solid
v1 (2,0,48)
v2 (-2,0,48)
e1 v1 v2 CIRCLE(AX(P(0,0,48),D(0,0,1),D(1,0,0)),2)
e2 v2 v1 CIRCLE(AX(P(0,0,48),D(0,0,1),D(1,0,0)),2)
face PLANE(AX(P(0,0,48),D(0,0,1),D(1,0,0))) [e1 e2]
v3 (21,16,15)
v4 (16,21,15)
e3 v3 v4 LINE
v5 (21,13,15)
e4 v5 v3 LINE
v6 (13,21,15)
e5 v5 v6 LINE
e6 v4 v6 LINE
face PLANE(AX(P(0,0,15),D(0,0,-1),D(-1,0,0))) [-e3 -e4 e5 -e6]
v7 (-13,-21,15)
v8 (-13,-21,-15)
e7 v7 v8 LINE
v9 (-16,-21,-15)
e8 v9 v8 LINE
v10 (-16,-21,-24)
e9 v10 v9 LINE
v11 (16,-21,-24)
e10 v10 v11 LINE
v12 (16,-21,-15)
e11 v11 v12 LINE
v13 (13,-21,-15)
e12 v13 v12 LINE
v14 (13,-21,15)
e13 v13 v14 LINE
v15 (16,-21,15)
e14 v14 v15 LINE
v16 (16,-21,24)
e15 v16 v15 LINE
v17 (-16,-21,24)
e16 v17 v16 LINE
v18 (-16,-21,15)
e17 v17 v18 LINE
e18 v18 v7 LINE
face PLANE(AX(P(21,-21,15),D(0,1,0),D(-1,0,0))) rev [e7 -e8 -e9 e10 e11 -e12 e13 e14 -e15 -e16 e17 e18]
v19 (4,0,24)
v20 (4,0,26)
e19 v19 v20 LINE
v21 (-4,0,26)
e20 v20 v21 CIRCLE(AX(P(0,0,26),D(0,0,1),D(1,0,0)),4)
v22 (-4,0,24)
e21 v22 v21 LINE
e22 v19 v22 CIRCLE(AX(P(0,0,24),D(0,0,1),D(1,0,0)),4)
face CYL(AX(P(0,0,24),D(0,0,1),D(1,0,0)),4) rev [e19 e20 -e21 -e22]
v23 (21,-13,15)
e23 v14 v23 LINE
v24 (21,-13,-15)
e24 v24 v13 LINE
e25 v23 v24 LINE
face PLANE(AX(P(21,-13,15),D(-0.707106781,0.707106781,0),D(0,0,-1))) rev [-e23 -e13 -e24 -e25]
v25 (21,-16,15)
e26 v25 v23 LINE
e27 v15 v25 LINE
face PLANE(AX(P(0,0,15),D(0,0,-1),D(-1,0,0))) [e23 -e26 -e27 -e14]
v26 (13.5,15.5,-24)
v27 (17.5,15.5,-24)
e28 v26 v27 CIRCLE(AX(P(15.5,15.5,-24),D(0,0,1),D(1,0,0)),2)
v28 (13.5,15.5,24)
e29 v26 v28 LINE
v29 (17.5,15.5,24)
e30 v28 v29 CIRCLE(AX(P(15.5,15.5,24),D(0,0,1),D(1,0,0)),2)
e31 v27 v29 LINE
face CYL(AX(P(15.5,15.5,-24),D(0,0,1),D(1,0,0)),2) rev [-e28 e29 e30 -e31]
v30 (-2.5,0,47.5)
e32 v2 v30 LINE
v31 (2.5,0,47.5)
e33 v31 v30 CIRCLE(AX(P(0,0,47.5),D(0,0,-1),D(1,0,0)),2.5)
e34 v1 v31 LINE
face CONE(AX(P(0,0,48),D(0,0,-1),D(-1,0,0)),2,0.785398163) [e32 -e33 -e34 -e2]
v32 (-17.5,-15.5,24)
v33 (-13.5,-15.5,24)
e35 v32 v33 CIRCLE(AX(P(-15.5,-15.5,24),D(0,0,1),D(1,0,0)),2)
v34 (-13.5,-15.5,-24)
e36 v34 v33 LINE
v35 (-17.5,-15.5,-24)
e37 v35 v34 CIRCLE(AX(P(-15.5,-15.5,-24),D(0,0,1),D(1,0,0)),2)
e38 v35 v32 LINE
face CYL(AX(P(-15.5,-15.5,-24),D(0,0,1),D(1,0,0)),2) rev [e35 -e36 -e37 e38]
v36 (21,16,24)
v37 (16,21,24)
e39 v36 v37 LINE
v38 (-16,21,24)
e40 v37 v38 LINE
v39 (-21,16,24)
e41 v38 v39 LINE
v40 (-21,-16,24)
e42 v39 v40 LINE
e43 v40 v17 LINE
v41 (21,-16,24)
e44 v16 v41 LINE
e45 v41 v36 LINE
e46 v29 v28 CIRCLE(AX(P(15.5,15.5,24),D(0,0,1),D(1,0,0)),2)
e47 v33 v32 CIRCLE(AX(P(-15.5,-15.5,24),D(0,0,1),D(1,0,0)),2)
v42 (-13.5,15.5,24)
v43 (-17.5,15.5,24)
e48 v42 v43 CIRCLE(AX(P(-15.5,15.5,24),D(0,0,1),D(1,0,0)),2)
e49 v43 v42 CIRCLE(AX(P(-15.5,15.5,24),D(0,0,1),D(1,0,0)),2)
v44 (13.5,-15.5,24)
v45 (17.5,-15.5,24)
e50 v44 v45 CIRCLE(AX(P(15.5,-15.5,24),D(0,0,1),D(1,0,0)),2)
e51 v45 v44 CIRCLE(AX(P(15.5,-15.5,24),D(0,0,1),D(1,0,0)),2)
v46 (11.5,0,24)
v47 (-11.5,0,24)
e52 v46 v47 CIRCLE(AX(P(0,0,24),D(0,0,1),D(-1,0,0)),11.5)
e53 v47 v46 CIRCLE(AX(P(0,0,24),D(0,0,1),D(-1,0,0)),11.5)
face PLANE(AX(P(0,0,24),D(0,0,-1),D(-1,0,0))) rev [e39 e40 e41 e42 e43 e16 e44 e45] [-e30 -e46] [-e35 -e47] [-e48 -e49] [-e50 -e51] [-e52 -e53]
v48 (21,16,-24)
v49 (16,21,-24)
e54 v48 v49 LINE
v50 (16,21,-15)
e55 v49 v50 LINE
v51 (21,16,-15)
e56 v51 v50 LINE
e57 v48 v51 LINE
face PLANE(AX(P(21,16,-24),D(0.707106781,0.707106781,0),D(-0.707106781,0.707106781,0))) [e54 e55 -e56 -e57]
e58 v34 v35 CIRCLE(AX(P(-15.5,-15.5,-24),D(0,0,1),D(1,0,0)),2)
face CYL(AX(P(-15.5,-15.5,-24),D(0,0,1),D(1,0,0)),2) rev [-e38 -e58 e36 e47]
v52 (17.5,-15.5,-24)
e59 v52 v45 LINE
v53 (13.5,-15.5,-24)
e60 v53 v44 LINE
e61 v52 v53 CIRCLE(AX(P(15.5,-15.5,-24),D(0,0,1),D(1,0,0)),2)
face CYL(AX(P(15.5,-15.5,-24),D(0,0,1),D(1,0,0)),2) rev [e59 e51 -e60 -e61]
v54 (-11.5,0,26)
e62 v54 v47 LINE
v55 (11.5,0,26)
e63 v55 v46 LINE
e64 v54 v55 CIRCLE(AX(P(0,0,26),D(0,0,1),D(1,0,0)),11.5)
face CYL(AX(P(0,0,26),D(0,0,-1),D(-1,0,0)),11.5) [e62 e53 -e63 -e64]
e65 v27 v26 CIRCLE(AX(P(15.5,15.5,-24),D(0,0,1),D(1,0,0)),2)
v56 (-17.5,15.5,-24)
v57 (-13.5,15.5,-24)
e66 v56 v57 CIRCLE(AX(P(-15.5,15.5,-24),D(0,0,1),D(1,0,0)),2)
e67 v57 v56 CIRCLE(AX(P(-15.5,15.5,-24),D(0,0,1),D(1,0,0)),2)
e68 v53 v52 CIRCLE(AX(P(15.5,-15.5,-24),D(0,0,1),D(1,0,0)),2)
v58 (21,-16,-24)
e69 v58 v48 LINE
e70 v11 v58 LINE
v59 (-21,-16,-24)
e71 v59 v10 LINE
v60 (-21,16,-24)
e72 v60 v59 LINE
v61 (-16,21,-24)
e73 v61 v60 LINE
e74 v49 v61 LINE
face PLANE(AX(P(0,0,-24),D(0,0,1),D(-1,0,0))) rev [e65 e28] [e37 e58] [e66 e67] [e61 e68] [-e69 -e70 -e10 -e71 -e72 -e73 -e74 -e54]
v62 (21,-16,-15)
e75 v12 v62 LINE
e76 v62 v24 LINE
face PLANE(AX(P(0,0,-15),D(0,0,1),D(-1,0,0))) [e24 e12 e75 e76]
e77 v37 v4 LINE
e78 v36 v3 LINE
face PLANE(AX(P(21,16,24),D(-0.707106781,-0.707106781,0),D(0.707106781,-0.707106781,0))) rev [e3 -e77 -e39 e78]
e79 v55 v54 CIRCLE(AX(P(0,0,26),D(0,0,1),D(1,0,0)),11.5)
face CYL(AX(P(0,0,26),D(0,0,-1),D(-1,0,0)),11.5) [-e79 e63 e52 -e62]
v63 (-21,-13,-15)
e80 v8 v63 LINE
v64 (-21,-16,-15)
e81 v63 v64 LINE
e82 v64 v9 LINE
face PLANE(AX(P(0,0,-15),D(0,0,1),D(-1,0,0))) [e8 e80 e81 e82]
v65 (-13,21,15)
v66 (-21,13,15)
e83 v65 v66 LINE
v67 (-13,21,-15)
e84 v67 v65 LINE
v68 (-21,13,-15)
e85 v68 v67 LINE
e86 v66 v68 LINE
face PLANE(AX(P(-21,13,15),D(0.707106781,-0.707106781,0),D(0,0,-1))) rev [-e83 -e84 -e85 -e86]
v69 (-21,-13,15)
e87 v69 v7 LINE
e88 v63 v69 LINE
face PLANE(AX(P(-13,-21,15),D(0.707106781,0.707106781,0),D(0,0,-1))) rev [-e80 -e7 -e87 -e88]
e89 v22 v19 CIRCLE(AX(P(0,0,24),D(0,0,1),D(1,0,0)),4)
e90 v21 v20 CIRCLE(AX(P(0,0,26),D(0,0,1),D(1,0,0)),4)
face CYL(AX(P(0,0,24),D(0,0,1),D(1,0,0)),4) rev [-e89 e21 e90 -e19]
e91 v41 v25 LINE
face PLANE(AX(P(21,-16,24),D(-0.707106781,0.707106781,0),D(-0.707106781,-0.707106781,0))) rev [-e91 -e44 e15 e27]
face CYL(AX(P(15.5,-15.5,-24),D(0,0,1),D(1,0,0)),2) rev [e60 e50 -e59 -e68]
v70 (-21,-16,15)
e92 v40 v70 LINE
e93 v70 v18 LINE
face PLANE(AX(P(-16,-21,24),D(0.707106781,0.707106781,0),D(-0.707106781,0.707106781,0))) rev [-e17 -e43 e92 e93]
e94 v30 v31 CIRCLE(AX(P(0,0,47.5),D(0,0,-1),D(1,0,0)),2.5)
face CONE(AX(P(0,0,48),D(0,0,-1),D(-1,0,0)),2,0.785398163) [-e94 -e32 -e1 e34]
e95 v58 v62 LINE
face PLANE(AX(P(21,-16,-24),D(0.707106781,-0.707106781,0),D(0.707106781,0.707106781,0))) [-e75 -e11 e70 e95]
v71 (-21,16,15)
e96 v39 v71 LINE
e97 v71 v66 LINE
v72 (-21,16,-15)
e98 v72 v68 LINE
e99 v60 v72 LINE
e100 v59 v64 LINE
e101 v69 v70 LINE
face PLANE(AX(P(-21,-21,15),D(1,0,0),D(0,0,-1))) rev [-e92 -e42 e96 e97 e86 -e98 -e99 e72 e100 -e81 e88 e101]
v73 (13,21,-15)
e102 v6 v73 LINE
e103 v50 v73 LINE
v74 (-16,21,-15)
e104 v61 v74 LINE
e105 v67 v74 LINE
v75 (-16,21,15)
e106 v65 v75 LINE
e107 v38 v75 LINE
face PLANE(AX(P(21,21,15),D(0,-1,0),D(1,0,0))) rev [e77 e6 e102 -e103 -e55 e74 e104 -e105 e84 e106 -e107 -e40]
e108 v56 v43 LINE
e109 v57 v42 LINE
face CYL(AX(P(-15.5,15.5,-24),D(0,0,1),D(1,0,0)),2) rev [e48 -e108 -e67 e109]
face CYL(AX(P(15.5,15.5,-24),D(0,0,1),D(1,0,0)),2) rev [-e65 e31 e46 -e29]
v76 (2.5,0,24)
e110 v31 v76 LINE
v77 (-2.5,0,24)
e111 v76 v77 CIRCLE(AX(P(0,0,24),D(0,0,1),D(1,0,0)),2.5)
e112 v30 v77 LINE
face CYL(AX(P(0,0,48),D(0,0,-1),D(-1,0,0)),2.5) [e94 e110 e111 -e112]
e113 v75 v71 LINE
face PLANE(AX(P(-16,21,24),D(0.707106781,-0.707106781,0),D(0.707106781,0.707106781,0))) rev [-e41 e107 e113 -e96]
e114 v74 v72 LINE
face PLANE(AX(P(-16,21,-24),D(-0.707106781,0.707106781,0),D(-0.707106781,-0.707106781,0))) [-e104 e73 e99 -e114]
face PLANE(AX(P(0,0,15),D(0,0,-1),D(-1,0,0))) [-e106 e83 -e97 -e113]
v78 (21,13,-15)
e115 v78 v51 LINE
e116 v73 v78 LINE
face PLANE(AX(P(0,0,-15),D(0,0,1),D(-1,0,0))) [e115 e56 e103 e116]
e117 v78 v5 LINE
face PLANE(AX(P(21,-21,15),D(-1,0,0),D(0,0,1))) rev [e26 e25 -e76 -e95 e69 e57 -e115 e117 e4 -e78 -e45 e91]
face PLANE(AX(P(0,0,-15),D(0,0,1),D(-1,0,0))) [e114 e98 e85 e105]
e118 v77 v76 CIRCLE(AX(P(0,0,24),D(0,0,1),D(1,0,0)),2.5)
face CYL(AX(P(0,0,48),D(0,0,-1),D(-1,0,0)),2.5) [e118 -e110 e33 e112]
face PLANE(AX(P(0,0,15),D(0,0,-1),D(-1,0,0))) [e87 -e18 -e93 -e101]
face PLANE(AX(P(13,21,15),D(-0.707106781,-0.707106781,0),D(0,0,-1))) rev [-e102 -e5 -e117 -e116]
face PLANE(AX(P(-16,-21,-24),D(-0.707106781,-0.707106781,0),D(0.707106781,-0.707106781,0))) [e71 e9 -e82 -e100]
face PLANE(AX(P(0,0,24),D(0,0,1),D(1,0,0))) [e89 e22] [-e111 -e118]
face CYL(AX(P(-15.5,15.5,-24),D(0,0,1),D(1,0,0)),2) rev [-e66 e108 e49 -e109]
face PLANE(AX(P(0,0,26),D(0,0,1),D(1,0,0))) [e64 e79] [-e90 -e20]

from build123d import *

# Parameters (mm, degrees)
SKETCH1_W           = 42
SKETCH1_H           = 42
BOSS_EXTRUDE1_DEPTH = 15
CHAMFER1_SIZE       = 8
BOSS_EXTRUDE2_DEPTH = 9
SKETCH4_R           = 11.5
BOSS_EXTRUDE3_DEPTH = 2
SKETCH5_R           = 2.5
BOSS_EXTRUDE4_DEPTH = 22
CUT_EXTRUDE1_START  = -2
SKETCH6_R           = 4
SKETCH6_R_2         = 2.5
CUT_EXTRUDE1_DEPTH  = 2
CHAMFER2_SIZE       = 0.5
SKETCH7_R           = 2
CUT_EXTRUDE2_DEPTH  = 57.444663167


with BuildPart() as part:
    # Sketch1 → Boss-Extrude1 (new, symmetric)
    with BuildSketch(Plane.XY):
        Rectangle(SKETCH1_W, SKETCH1_H)
    extrude(amount=BOSS_EXTRUDE1_DEPTH, both=True)

    # Chamfer1
    chamfer1_edges = [part.edges().sort_by_distance(p)[0] for p in [
        (-21, 21, 0),
        (21, 21, 0),
        (21, -21, 0),
        (-21, -21, 0),
    ]]
    chamfer(chamfer1_edges, length=CHAMFER1_SIZE)

    # Sketch3 → Boss-Extrude2 (add)
    with BuildSketch(Plane.XY.offset(15)):
        Polygon((16, -21), (-16, -21), (-21, -16), (-21, 16), (-16, 21), (16, 21), (21, 16), (21, -16), align=None)
    boss_extrude2 = extrude(amount=BOSS_EXTRUDE2_DEPTH)

    # Mirror1: Boss-Extrude2 across plane
    add(boss_extrude2.mirror(Plane.XY))

    # Sketch4 → Boss-Extrude3 (add)
    with BuildSketch(Plane.XY.offset(24)):
        with Locations(Location((0, 0, 0), (0, 0, 180))):
            Circle(SKETCH4_R)
    extrude(amount=BOSS_EXTRUDE3_DEPTH)

    # Sketch5 → Boss-Extrude4 (add)
    with BuildSketch(Plane.XY.offset(26)):
        Circle(SKETCH5_R)
    extrude(amount=BOSS_EXTRUDE4_DEPTH)

    # Sketch6 → Cut-Extrude1 (cut)
    with BuildSketch(Plane.XY.offset(26).offset(CUT_EXTRUDE1_START)):
        Circle(SKETCH6_R)
        Circle(SKETCH6_R_2, mode=Mode.SUBTRACT)
    extrude(amount=CUT_EXTRUDE1_DEPTH, mode=Mode.SUBTRACT)

    # Chamfer2
    chamfer2_edges = [part.edges().sort_by_distance(p)[0] for p in [
        (-2.5, 0, 48),
    ]]
    chamfer(chamfer2_edges, length=CHAMFER2_SIZE)

    # Sketch7 → Cut-Extrude2 (cut, through all)
    with BuildSketch(Plane.XY.offset(24)):
        with Locations((15.5, 15.5)):
            Circle(SKETCH7_R)
        with Locations((15.5, -15.5)):
            Circle(SKETCH7_R)
        with Locations((-15.5, -15.5)):
            Circle(SKETCH7_R)
        with Locations((-15.5, 15.5)):
            Circle(SKETCH7_R)
    extrude(amount=-CUT_EXTRUDE2_DEPTH, mode=Mode.SUBTRACT)


solid = part.part
